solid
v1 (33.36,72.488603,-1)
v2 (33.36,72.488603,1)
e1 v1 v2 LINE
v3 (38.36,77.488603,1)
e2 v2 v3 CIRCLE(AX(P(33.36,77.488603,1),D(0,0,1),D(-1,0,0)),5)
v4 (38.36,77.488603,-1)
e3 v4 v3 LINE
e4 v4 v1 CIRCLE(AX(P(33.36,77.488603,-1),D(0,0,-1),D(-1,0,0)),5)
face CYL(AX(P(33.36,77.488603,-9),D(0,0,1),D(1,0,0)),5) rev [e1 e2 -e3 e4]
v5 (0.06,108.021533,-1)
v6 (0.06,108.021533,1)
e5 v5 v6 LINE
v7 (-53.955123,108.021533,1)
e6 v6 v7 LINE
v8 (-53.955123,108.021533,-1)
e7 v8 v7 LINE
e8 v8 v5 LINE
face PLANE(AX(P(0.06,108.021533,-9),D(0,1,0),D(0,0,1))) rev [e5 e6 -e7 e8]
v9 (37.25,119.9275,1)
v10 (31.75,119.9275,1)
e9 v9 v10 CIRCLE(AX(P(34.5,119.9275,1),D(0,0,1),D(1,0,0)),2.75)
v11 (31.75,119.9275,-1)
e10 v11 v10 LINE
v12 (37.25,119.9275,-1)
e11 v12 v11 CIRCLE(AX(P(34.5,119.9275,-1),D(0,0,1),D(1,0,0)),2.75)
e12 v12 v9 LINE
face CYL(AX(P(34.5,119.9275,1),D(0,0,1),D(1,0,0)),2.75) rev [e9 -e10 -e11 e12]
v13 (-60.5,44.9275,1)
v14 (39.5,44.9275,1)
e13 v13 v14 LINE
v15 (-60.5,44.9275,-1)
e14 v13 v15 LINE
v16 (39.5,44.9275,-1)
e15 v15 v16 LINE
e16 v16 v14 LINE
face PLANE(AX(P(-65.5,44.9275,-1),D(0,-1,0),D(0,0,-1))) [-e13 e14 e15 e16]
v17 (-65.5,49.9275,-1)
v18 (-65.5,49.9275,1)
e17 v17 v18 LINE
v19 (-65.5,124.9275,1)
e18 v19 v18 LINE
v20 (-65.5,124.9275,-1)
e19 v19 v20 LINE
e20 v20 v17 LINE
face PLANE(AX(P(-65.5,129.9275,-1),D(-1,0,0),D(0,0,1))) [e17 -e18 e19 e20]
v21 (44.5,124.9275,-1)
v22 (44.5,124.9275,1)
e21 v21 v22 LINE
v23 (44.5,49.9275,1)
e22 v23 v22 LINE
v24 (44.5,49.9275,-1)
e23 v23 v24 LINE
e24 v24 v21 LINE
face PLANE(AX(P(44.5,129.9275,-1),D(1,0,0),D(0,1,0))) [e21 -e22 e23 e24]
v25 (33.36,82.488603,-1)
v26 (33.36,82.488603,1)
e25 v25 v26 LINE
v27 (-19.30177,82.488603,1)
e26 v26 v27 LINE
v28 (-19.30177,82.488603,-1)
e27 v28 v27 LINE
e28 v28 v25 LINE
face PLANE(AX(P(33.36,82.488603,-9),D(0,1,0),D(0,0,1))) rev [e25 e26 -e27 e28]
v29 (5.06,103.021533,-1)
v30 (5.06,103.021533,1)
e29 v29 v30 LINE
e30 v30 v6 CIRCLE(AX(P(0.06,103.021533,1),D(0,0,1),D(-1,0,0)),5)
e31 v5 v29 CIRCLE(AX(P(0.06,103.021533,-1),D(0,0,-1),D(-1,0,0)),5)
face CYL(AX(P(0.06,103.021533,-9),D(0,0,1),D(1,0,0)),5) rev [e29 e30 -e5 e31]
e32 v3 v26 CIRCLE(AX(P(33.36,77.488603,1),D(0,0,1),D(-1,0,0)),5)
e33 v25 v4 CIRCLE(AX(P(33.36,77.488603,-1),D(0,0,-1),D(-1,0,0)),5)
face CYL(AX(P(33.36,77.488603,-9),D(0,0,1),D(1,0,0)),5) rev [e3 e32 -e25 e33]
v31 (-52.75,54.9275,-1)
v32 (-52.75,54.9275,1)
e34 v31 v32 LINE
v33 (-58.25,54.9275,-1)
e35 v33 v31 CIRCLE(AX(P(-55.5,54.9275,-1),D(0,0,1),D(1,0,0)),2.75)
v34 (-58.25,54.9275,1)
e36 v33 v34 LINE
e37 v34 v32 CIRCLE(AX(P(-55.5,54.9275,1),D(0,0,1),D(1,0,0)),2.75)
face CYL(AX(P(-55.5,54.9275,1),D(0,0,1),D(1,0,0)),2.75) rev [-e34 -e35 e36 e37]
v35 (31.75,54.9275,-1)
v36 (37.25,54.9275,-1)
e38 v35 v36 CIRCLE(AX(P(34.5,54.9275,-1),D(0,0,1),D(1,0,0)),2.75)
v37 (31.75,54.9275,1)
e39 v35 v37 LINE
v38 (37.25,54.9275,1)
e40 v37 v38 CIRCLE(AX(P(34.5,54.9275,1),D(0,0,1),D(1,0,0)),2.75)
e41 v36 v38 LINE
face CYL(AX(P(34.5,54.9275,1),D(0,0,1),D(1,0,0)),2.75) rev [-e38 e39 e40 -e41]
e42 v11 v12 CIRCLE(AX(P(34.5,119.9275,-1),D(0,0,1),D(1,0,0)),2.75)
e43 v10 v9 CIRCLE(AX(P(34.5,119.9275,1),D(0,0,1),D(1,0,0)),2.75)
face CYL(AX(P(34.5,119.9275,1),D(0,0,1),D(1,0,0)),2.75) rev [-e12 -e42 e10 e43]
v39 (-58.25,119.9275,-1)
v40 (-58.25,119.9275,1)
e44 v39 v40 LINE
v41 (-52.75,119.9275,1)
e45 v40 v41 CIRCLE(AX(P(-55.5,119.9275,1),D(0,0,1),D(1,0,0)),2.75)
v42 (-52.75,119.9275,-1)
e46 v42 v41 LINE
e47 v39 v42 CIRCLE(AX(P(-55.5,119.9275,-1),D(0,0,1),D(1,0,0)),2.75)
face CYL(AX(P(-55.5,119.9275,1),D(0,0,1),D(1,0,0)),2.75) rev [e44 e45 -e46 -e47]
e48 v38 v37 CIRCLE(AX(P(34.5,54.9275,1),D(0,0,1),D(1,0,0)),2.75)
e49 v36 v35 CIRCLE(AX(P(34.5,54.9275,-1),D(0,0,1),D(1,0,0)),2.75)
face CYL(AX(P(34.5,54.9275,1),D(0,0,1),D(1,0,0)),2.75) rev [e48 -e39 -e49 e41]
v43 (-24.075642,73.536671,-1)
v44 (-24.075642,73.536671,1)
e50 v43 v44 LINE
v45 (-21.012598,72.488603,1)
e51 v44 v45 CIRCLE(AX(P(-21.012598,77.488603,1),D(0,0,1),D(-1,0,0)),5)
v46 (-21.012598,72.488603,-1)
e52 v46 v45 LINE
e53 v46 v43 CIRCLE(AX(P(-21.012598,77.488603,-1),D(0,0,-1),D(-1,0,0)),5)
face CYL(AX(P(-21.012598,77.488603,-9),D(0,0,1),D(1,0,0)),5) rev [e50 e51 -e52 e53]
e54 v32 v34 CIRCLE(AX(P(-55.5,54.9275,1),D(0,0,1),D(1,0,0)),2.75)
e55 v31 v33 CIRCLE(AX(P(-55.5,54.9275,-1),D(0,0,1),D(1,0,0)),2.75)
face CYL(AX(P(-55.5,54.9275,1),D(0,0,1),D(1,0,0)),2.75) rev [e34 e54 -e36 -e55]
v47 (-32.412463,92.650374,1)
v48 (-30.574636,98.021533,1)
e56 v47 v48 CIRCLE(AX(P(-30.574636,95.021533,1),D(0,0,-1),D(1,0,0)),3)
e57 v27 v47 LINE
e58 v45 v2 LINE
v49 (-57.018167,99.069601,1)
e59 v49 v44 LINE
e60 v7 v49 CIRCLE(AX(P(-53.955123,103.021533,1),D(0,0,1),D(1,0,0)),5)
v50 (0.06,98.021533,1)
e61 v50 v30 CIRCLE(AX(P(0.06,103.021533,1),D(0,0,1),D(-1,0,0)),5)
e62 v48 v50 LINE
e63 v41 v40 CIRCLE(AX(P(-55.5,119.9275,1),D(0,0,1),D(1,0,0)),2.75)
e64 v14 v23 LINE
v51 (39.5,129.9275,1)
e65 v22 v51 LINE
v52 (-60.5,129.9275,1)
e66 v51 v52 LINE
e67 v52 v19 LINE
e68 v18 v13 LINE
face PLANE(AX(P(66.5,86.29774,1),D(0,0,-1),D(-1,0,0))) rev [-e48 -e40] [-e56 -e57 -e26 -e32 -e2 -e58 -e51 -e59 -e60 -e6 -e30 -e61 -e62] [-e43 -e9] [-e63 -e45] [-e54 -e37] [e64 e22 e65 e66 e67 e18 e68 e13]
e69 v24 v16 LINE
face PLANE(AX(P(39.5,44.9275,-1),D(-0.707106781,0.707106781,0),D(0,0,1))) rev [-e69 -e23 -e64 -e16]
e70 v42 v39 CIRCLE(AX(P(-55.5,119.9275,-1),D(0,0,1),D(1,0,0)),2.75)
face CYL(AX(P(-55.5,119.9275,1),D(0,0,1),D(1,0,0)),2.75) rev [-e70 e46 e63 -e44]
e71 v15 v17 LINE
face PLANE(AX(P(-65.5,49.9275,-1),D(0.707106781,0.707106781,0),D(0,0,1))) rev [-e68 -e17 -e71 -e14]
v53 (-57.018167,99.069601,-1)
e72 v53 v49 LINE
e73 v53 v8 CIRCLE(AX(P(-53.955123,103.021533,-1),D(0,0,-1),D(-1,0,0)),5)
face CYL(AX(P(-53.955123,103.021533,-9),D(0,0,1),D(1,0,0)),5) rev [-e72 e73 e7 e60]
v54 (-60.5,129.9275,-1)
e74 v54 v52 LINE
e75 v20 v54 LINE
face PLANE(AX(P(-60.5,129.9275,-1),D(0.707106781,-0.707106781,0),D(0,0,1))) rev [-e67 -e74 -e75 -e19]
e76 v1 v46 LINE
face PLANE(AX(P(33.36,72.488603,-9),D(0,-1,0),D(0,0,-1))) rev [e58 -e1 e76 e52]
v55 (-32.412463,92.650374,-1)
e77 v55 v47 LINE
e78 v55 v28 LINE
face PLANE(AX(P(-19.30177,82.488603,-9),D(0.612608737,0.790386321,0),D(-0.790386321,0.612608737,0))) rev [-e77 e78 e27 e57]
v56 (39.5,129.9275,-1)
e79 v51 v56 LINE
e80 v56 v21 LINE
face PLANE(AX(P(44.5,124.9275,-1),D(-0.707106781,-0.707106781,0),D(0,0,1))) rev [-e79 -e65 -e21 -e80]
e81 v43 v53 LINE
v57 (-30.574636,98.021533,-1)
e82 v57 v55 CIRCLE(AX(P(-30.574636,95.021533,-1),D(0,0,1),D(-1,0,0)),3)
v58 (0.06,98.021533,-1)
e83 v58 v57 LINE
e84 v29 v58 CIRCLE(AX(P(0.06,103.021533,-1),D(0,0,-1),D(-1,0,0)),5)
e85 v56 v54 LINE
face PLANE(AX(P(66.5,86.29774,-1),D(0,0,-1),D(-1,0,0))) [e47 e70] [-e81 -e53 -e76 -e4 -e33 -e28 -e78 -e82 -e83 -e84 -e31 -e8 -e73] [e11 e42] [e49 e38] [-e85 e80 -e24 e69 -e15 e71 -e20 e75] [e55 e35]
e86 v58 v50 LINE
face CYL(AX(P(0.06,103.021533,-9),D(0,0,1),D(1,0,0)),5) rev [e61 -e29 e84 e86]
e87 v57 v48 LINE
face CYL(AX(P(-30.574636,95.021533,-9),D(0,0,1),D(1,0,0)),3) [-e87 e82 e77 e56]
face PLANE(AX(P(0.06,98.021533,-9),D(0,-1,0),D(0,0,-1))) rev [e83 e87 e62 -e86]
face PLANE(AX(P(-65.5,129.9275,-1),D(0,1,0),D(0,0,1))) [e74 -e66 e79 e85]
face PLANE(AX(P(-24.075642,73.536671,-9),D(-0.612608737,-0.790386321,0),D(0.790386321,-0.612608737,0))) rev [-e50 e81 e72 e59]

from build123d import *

# Parameters (mm, degrees)
EXTRUDE_1_DEPTH              = 1
HOLE_WIZARD_M6_1_D           = 6.6
HOLE_WIZARD_M6_1_CBORE_D     = 11
HOLE_WIZARD_M6_1_CBORE_DEPTH = 6.4
SKETCH_27_W                  = 153
SKETCH_27_H                  = 120
EXTRUDE_3_DEPTH              = 2
HOLE_WIZARD_M5_2_D           = 4.2
HOLE_WIZARD_M5_2_DEPTH       = 14
HOLE_WIZARD_M5_2_TIP         = 1.2618073
SKETCH_15_W                  = 112.889805259
SKETCH_15_H                  = 130.002769253
CUT_EXTRUDE_1_DEPTH          = 512.721848273
SKETCH_16_R                  = 10
CUT_EXTRUDE_2_DEPTH          = 2
SKETCH_18_R                  = 10
CUT_EXTRUDE_4_DEPTH          = 2
SKETCH_28_W                  = 266.209573984
SKETCH_28_H                  = 254.96875003
CUT_EXTRUDE_7_DEPTH          = 512.721848273
SKETCH_29_W                  = 20
SKETCH_29_H                  = 197
EXTRUDE_4_DEPTH              = 2
SKETCH_30_W                  = 160
SKETCH_30_H                  = 28
EXTRUDE_5_DEPTH              = 2
SKETCH_31_W                  = 160
SKETCH_31_H                  = 323
CUT_EXTRUDE_8_DEPTH          = 471.473431768
SKETCH_32_W                  = 27
SKETCH_32_H                  = 140
CUT_EXTRUDE_9_DEPTH          = 164.022237747
SKETCH_33_R                  = 10
EXTRUDE_6_DEPTH              = 2
EXTRUDE_7_DEPTH              = 2
HOLE_WIZARD_M6_2_D           = 6.6
HOLE_WIZARD_M6_2_CBORE_D     = 11
HOLE_WIZARD_M6_2_CBORE_DEPTH = 6.4
SKETCH_38_W                  = 13
SKETCH_38_H                  = 160
CUT_EXTRUDE_10_DEPTH         = 10
SKETCH_39_W                  = 50
SKETCH_39_H                  = 110.0725
EXTRUDE_8_DEPTH              = 2
SKETCH_40_W                  = 120
SKETCH_40_H                  = 49.9275
CUT_EXTRUDE_11_DEPTH         = 185.727502013
HOLE_WIZARD_5_5_5_5_1_D      = 5.5
MOVE_FACE_1_BY               = 7.5
MOVE_FACE_2_BY               = 7.5
FILLET_4_R                   = 10
SKETCH_44_OUTSIDE_W          = 214.212
SKETCH_44_OUTSIDE_H          = 169.284
SKETCH_44_OUTSIDE_W_2        = 110
SKETCH_44_OUTSIDE_H_2        = 85
CUT_EXTRUDE_12_DEPTH         = 191.47440773
CHAMFER_1_SIZE               = 5
HOLE_WIZARD_5_5_5_5_2_D      = 5.5
CUT_EXTRUDE_13_DEPTH         = 10


with BuildPart() as part:
    # Model → 凸台-拉伸1 (new, symmetric)
    with BuildSketch(Plane.XY):
        with BuildLine():
            Line((186.507023758, 241.511944981), (58.910891188, 92.809685219))
            ThreePointArc((58.910891188, 92.809685219), (57.122071441, 89.769692994), (56.5, 86.297740238))
            Line((56.5, 86.297740238), (56.5, 0))
            Line((56.5, 0), (-73.5, 0))
            ThreePointArc((-73.5, 0), (-80.571067812, 2.928932188), (-83.5, 10))
            Line((-83.5, 10), (-83.5, 335))
            Line((-83.5, 335), (59.5, 335))
            ThreePointArc((59.5, 335), (66.571067812, 337.928932188), (69.5, 345))
            Line((69.5, 345), (69.5, 435))
            Line((69.5, 435), (259.5, 435))
            ThreePointArc((259.5, 435), (266.571067812, 432.071067812), (269.5, 425))
            Line((269.5, 425), (269.5, 255))
            ThreePointArc((269.5, 255), (266.571067812, 247.928932188), (259.5, 245))
            Line((259.5, 245), (194.09613257, 245))
            ThreePointArc((194.09613257, 245), (189.91997703, 244.086238215), (186.507023758, 241.511944981))
        make_face()
    extrude(amount=EXTRUDE_1_DEPTH, both=True)

    # M6 六角凹头螺钉的柱形沉头孔1 (through all)
    with Locations(Plane(origin=(0, 0, -1), x_dir=(-1, 0, 0), z_dir=(0, 0, -1))):
        with Locations((16.5, 157), (-9.5, 235), (-9.5, 157), (16.5, 235)):
            CounterBoreHole(HOLE_WIZARD_M6_1_D / 2, HOLE_WIZARD_M6_1_CBORE_D / 2, HOLE_WIZARD_M6_1_CBORE_DEPTH)

    # 草图27 → 凸台-拉伸3 (add)
    with BuildSketch(Plane.XY.offset(1)):
        with Locations((-7, 375)):
            Rectangle(SKETCH_27_W, SKETCH_27_H)
    extrude(amount=-EXTRUDE_3_DEPTH)

    # M5 螺纹孔2
    with Locations(Plane.XY.offset(1)):
        with Locations((-60.5, 390), (27.5, 405), (47.5, 265), (-32.5, 270)):
            Hole(HOLE_WIZARD_M5_2_D / 2, depth=HOLE_WIZARD_M5_2_DEPTH)
            with Locations((0, 0, -(HOLE_WIZARD_M5_2_DEPTH + HOLE_WIZARD_M5_2_TIP / 2))):  # 118° drill point
                Cone(0, HOLE_WIZARD_M5_2_D / 2, HOLE_WIZARD_M5_2_TIP, mode=Mode.SUBTRACT)

    # 草图15 → 切除-拉伸1 (cut, through all)
    with BuildSketch(Plane.XY.offset(1)):
        with Locations((112.94490263, 131.998615374)):
            Rectangle(SKETCH_15_W, SKETCH_15_H)
    extrude(amount=-CUT_EXTRUDE_1_DEPTH, mode=Mode.SUBTRACT)

    # 草图16 → 切除-拉伸2 (cut)
    with BuildSketch(Plane.XY.offset(1)):
        with Locations((-13.5, 25)):
            Circle(SKETCH_16_R)
    cut_extrude_2 = extrude(amount=-CUT_EXTRUDE_2_DEPTH, mode=Mode.SUBTRACT)

    # 草图18 → 切除-拉伸4 (cut)
    with BuildSketch(Plane.XY.offset(1)):
        with Locations((244.5, 340)):
            Circle(SKETCH_18_R)
    extrude(amount=-CUT_EXTRUDE_4_DEPTH, mode=Mode.SUBTRACT)

    # 草图28 → 切除-拉伸7 (cut, through all)
    with BuildSketch(Plane.XY.offset(1)):
        with Locations((209.604786992, 307.515624985)):
            Rectangle(SKETCH_28_W, SKETCH_28_H)
    extrude(amount=-CUT_EXTRUDE_7_DEPTH, mode=Mode.SUBTRACT)

    # 草图29 → 凸台-拉伸4 (add)
    with BuildSketch(Plane.XY.offset(1)):
        with Locations((66.5, 98.5)):
            Rectangle(SKETCH_29_W, SKETCH_29_H)
    extrude(amount=-EXTRUDE_4_DEPTH)

    # 草图30 → 凸台-拉伸5 (add)
    with BuildSketch(Plane.XY.offset(1)):
        with Locations((-3.5, 449)):
            Rectangle(SKETCH_30_W, SKETCH_30_H)
    extrude(amount=-EXTRUDE_5_DEPTH)

    # 镜向1: 切除-拉伸2 across plane
    add(cut_extrude_2.mirror(Plane.ZX.offset(231.5)), mode=Mode.SUBTRACT)

    # 草图31 → 切除-拉伸8 (cut, through all)
    with BuildSketch(Plane.XY.offset(1)):
        with Locations((-3.5, 301.5)):
            Rectangle(SKETCH_31_W, SKETCH_31_H)
    extrude(amount=-CUT_EXTRUDE_8_DEPTH, mode=Mode.SUBTRACT)

    # 草图32 → 切除-拉伸9 (cut, through all)
    with BuildSketch(Plane.XY.offset(1)):
        with Locations((63, 70)):
            Rectangle(SKETCH_32_W, SKETCH_32_H)
    extrude(amount=-CUT_EXTRUDE_9_DEPTH, mode=Mode.SUBTRACT)

    # 草图33 → 凸台-拉伸6 (add)
    with BuildSketch(Plane.XY.offset(1)):
        with Locations((-13.5, 25)):
            Circle(SKETCH_33_R)
    extrude(amount=-EXTRUDE_6_DEPTH)

    # 草图37 → 凸台-拉伸7 (add)
    with BuildSketch(Plane.XY.offset(1)):
        with BuildLine():
            Line((49.5, 0), (-73.5, 0))
            ThreePointArc((-73.5, 0), (-80.571067812, 2.928932188), (-83.5, 10))
            Line((-83.5, 10), (-83.5, -20))
            Line((-83.5, -20), (49.5, -20))
            Line((49.5, -20), (49.5, 0))
        make_face()
    extrude(amount=-EXTRUDE_7_DEPTH)

    # M6 六角凹头螺钉的柱形沉头孔2 (through all)
    with Locations(Plane.XY.offset(1)):
        with Locations((-40.5, -10), (-40.5, 15), (19.5, 15), (19.5, -10)):
            CounterBoreHole(HOLE_WIZARD_M6_2_D / 2, HOLE_WIZARD_M6_2_CBORE_D / 2, HOLE_WIZARD_M6_2_CBORE_DEPTH)

    # 草图38 → 切除-拉伸10 (cut)
    with BuildSketch(Plane.XY.offset(1)):
        with Locations((-77, 60)):
            Rectangle(SKETCH_38_W, SKETCH_38_H)
    extrude(amount=-CUT_EXTRUDE_10_DEPTH, mode=Mode.SUBTRACT)

    # 草图39 → 凸台-拉伸8 (add)
    with BuildSketch(Plane.XY.offset(1)):
        with Locations((-95.5, 84.96375)):
            Rectangle(SKETCH_39_W, SKETCH_39_H)
    extrude(amount=-EXTRUDE_8_DEPTH)

    # 草图40 → 切除-拉伸11 (cut, through all)
    with BuildSketch(Plane(origin=(0, 0, -1), x_dir=(-1, 0, 0), z_dir=(0, 0, -1))):
        with Locations((10.5, 4.96375)):
            Rectangle(SKETCH_40_W, SKETCH_40_H)
    extrude(amount=-CUT_EXTRUDE_11_DEPTH, mode=Mode.SUBTRACT)

    # Ø5.5 (5.5) 直径孔1 (through all)
    with Locations(Plane.XY.offset(1)):
        with Locations((-87.5, 57.4275), (-112.5, 57.4275), (-112.5, 117.4275), (-87.5, 117.4275)):
            Hole(HOLE_WIZARD_5_5_5_5_1_D / 2)

    # Move Face 1: a face moved outward by 7.5
    extrude(part.faces().sort_by_distance((-35.5, 29.9275, 0))[0], amount=MOVE_FACE_1_BY, dir=(0, -1, 0))

    # Move Face 2: a face moved outward by 7.5
    extrude(part.faces().sort_by_distance((-35.5, 140, 0))[0], amount=MOVE_FACE_2_BY, dir=(0, 1, 0))

    # 圆角4
    fillet_4_edges = [part.edges().sort_by_distance(p)[0] for p in [
        (49.5, 147.5, 0),
        (-120.5, 147.5, 0),
        (-120.5, 22.4275, 0),
        (49.5, 22.4275, 0),
    ]]
    fillet(fillet_4_edges, radius=FILLET_4_R)

    # 草图44 outside → 切除-拉伸12 (cut, through all)
    with BuildSketch(Plane.XY.offset(1)):
        with Locations((-35.5, 84.964)):
            Rectangle(SKETCH_44_OUTSIDE_W, SKETCH_44_OUTSIDE_H)
        with Locations((-10.5, 87.4275)):
            Rectangle(SKETCH_44_OUTSIDE_W_2, SKETCH_44_OUTSIDE_H_2, mode=Mode.SUBTRACT)
    extrude(amount=-CUT_EXTRUDE_12_DEPTH, mode=Mode.SUBTRACT)

    # 倒角1
    chamfer_1_edges = [part.edges().sort_by_distance(p)[0] for p in [
        (-65.5, 129.9275, 0),
        (44.5, 129.9275, 0),
        (44.5, 44.9275, 0),
        (-65.5, 44.9275, 0),
    ]]
    chamfer(chamfer_1_edges, length=CHAMFER_1_SIZE)

    # Ø5.5 (5.5) 直径孔2 (through all)
    with Locations(Plane.XY.offset(1)):
        with Locations((34.5, 54.9275), (34.5, 119.9275), (-55.5, 119.9275), (-55.5, 54.9275)):
            Hole(HOLE_WIZARD_5_5_5_5_2_D / 2)

    # 草图45 → 切除-拉伸13 (cut)
    with BuildSketch(Plane.XY.offset(1)):
        with BuildLine():
            Line((33.36, 72.488602629), (-21.012598119, 72.488602629))
            ThreePointArc((-21.012598119, 72.488602629), (-22.631292343, 72.757870233), (-24.075641802, 73.536671027))
            Line((-24.075641802, 73.536671027), (-57.018167055, 99.06960126))
            ThreePointArc((-57.018167055, 99.06960126), (-58.685855768, 104.640227087), (-53.955123371, 108.021532863))
            Line((-53.955123371, 108.021532863), (0.06, 108.021532863))
            ThreePointArc((0.06, 108.021532863), (5.06, 103.021532863), (0.06, 98.021532863))
            Line((0.06, 98.021532863), (-30.574636438, 98.021532863))
            ThreePointArc((-30.574636438, 98.021532863), (-33.413075876, 95.992749398), (-32.412462648, 92.650373901))
            Line((-32.412462648, 92.650373901), (-19.301769764, 82.488602629))
            Line((-19.301769764, 82.488602629), (33.36, 82.488602629))
            ThreePointArc((33.36, 82.488602629), (38.36, 77.488602629), (33.36, 72.488602629))
        make_face()
    extrude(amount=-CUT_EXTRUDE_13_DEPTH, mode=Mode.SUBTRACT)


solid = part.part
